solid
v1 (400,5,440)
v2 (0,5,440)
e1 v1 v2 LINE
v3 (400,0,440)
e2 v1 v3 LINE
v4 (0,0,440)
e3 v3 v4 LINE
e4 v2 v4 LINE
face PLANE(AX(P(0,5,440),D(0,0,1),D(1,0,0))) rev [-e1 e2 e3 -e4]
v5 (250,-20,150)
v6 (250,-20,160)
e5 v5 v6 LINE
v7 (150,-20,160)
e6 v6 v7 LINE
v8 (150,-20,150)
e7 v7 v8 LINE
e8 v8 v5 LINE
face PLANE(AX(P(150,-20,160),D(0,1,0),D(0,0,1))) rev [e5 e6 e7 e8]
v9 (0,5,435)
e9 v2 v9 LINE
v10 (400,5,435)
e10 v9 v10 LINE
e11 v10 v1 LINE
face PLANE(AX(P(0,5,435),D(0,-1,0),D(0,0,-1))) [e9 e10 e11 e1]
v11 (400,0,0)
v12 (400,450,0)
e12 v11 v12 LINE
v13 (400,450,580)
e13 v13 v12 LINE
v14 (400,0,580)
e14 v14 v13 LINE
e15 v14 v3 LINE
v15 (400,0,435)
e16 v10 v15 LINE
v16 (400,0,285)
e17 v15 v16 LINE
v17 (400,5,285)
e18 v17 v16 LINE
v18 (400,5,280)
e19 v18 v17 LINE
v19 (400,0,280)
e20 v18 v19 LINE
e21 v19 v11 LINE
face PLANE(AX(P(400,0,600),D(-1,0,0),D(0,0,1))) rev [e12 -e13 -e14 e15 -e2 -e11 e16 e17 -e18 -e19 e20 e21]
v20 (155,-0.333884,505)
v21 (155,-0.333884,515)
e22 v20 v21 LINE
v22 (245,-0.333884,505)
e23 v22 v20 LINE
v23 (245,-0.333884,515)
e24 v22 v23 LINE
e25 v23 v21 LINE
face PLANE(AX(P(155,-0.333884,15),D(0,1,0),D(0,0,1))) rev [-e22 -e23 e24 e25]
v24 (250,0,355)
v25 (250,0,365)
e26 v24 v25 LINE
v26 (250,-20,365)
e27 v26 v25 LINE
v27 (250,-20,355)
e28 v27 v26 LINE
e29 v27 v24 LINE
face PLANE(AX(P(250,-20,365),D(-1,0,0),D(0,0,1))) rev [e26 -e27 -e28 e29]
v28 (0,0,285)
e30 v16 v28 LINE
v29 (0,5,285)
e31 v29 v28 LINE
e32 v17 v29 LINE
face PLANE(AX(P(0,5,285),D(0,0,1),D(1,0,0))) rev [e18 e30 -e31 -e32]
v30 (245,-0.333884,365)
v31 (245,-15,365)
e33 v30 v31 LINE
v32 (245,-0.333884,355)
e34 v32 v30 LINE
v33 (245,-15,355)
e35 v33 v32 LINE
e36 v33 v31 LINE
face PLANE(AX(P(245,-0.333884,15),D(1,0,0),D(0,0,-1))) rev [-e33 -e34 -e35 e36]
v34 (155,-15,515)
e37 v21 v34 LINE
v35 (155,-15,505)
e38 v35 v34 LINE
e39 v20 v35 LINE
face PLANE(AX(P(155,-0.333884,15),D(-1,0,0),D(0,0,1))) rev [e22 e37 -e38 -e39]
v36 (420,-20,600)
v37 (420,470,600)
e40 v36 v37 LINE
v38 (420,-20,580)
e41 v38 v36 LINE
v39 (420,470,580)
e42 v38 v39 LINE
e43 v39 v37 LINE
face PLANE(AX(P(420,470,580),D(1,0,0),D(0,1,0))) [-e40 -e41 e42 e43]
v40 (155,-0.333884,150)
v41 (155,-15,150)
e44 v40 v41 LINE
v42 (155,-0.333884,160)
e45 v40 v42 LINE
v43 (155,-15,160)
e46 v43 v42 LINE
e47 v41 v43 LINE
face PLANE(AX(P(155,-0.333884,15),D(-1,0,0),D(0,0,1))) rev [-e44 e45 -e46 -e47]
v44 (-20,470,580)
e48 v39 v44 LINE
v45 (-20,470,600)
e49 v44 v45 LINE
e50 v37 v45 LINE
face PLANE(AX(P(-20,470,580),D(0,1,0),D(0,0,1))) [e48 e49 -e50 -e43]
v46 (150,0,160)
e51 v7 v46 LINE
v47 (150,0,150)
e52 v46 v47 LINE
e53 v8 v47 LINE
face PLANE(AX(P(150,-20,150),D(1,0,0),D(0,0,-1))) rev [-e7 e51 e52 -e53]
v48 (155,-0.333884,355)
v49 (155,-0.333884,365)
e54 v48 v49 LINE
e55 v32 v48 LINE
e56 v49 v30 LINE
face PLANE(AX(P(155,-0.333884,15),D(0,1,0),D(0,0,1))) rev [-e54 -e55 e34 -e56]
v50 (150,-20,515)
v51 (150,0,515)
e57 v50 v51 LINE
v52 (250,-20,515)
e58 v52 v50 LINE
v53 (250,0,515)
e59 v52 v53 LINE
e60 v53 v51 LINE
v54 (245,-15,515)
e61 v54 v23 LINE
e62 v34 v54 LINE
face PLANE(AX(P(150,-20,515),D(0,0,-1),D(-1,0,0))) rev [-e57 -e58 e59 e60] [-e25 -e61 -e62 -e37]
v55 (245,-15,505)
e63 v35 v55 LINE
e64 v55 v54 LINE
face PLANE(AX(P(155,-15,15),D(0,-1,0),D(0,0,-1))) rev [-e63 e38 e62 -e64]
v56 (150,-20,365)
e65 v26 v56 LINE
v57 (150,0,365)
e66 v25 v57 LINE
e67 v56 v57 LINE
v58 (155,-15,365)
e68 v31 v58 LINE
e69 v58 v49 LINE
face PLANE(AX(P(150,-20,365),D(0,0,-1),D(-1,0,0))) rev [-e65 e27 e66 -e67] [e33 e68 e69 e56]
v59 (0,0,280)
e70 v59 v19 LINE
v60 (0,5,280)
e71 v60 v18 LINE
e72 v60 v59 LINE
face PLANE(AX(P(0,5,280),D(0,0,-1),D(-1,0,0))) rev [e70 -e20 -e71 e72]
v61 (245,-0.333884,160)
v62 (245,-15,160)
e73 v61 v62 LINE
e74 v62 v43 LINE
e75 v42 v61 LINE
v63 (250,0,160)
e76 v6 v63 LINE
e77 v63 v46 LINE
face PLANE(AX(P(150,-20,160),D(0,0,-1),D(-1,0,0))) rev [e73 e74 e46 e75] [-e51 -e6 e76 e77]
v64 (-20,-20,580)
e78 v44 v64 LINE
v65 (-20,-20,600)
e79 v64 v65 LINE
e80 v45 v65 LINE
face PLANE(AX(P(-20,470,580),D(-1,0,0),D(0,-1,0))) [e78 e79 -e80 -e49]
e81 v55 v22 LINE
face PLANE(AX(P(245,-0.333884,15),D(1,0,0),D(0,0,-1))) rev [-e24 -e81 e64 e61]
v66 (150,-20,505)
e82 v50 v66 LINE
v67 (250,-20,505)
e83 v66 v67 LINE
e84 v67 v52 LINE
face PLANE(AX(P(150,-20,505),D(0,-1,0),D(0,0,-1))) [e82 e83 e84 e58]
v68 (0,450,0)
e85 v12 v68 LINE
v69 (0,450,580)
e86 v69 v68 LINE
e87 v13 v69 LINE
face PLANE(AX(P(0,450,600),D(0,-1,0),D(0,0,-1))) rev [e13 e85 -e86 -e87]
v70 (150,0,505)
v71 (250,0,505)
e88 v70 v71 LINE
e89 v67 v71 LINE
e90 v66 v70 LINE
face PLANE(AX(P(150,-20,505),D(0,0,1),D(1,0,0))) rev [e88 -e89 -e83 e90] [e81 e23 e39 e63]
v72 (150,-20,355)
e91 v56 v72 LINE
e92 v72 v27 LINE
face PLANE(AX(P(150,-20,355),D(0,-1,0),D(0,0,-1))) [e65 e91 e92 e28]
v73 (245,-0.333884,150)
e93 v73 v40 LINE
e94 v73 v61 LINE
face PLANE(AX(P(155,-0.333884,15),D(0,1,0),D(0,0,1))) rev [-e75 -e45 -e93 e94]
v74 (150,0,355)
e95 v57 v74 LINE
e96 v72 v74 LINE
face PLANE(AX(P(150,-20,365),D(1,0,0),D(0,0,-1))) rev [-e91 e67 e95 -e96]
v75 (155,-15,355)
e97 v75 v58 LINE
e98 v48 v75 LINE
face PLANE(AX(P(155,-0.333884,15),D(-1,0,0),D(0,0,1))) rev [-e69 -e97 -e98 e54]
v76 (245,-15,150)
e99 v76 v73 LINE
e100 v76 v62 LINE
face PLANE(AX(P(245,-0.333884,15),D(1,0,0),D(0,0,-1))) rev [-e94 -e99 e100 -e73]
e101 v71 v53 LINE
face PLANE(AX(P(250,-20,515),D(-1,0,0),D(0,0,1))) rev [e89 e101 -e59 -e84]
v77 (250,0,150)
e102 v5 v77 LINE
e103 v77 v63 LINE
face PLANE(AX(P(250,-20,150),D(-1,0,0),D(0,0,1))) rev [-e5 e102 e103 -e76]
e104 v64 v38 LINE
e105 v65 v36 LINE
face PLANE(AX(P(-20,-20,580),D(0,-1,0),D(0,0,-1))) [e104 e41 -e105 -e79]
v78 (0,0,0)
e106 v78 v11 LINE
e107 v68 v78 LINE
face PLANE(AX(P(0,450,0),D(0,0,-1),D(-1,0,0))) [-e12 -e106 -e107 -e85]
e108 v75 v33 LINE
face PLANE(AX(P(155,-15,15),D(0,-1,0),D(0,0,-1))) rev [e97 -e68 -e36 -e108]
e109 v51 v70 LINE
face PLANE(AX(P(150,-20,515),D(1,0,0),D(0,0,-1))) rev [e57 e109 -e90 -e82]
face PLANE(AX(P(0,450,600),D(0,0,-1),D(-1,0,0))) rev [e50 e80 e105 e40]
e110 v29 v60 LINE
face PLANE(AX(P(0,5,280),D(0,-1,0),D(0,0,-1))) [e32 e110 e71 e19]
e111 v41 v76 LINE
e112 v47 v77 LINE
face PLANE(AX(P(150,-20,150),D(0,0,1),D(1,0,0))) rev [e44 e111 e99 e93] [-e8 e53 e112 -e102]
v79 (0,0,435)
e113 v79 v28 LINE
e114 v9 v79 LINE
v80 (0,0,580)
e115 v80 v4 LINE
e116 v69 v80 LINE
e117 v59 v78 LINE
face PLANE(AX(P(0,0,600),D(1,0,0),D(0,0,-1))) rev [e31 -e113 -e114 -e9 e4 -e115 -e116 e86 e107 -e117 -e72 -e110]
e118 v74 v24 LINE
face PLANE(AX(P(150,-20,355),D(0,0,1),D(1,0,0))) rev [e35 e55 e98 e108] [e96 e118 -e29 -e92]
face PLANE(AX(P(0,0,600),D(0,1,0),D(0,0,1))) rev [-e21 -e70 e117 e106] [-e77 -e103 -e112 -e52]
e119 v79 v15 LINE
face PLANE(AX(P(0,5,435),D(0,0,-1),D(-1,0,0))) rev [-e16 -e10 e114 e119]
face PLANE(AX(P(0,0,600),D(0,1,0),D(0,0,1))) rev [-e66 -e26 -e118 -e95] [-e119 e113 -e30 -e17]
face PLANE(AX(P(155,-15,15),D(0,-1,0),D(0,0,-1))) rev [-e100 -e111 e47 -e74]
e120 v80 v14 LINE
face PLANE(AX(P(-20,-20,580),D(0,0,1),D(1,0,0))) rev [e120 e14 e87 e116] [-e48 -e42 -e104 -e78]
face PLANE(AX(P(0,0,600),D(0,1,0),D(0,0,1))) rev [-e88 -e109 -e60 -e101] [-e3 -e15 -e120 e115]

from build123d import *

# Parameters (mm, degrees)
SKETCH1_W           = 400
SKETCH1_H           = 450
BOSS_EXTRUDE1_DEPTH = 600
SKETCH2_W           = 440
SKETCH2_H           = 490
BOSS_EXTRUDE2_DEPTH = 20
SKETCH3_W           = 400
SKETCH3_H           = 5
CUT_EXTRUDE1_DEPTH  = 5
SKETCH4_W           = 400
SKETCH4_H           = 5
CUT_EXTRUDE2_DEPTH  = 5
SKETCH5_W           = 100
SKETCH5_H           = 10
BOSS_EXTRUDE3_DEPTH = 20
SKETCH6_W           = 100
SKETCH6_H           = 10
BOSS_EXTRUDE4_DEPTH = 20
SKETCH7_W           = 100
SKETCH7_H           = 10
BOSS_EXTRUDE5_DEPTH = 20
SKETCH8_W           = 90
SKETCH8_H           = 14.666116079
CUT_EXTRUDE3_DEPTH  = 500


with BuildPart() as part:
    # Sketch1 → Boss-Extrude1 (new body)
    with BuildSketch(Plane.XY):
        with Locations((200, 225)):
            Rectangle(SKETCH1_W, SKETCH1_H)
    extrude(amount=BOSS_EXTRUDE1_DEPTH)

    # Sketch2 → Boss-Extrude2 (add)
    with BuildSketch(Plane.XY.offset(600)):
        with Locations((200, 225)):
            Rectangle(SKETCH2_W, SKETCH2_H)
    extrude(amount=-BOSS_EXTRUDE2_DEPTH)

    # Sketch3 → Cut-Extrude1 (cut)
    with BuildSketch(Plane.XZ):
        with Locations((200, 437.5)):
            Rectangle(SKETCH3_W, SKETCH3_H)
    extrude(amount=-CUT_EXTRUDE1_DEPTH, mode=Mode.SUBTRACT)

    # Sketch4 → Cut-Extrude2 (cut)
    with BuildSketch(Plane.XZ):
        with Locations((200, 282.5)):
            Rectangle(SKETCH4_W, SKETCH4_H)
    extrude(amount=-CUT_EXTRUDE2_DEPTH, mode=Mode.SUBTRACT)

    # Sketch5 → Boss-Extrude3 (add)
    with BuildSketch(Plane.XZ):
        with Locations((200, 510)):
            Rectangle(SKETCH5_W, SKETCH5_H)
    extrude(amount=BOSS_EXTRUDE3_DEPTH)

    # Sketch6 → Boss-Extrude4 (add)
    with BuildSketch(Plane.XZ):
        with Locations((200, 360)):
            Rectangle(SKETCH6_W, SKETCH6_H)
    extrude(amount=BOSS_EXTRUDE4_DEPTH)

    # Sketch7 → Boss-Extrude5 (add)
    with BuildSketch(Plane.XZ):
        with Locations((200, 155)):
            Rectangle(SKETCH7_W, SKETCH7_H)
    extrude(amount=BOSS_EXTRUDE5_DEPTH)

    # Sketch8 → Cut-Extrude3 (cut)
    with BuildSketch(Plane.XY.offset(515)):
        with Locations((200, -7.666941961)):
            Rectangle(SKETCH8_W, SKETCH8_H)
    extrude(amount=-CUT_EXTRUDE3_DEPTH, mode=Mode.SUBTRACT)


solid = part.part
